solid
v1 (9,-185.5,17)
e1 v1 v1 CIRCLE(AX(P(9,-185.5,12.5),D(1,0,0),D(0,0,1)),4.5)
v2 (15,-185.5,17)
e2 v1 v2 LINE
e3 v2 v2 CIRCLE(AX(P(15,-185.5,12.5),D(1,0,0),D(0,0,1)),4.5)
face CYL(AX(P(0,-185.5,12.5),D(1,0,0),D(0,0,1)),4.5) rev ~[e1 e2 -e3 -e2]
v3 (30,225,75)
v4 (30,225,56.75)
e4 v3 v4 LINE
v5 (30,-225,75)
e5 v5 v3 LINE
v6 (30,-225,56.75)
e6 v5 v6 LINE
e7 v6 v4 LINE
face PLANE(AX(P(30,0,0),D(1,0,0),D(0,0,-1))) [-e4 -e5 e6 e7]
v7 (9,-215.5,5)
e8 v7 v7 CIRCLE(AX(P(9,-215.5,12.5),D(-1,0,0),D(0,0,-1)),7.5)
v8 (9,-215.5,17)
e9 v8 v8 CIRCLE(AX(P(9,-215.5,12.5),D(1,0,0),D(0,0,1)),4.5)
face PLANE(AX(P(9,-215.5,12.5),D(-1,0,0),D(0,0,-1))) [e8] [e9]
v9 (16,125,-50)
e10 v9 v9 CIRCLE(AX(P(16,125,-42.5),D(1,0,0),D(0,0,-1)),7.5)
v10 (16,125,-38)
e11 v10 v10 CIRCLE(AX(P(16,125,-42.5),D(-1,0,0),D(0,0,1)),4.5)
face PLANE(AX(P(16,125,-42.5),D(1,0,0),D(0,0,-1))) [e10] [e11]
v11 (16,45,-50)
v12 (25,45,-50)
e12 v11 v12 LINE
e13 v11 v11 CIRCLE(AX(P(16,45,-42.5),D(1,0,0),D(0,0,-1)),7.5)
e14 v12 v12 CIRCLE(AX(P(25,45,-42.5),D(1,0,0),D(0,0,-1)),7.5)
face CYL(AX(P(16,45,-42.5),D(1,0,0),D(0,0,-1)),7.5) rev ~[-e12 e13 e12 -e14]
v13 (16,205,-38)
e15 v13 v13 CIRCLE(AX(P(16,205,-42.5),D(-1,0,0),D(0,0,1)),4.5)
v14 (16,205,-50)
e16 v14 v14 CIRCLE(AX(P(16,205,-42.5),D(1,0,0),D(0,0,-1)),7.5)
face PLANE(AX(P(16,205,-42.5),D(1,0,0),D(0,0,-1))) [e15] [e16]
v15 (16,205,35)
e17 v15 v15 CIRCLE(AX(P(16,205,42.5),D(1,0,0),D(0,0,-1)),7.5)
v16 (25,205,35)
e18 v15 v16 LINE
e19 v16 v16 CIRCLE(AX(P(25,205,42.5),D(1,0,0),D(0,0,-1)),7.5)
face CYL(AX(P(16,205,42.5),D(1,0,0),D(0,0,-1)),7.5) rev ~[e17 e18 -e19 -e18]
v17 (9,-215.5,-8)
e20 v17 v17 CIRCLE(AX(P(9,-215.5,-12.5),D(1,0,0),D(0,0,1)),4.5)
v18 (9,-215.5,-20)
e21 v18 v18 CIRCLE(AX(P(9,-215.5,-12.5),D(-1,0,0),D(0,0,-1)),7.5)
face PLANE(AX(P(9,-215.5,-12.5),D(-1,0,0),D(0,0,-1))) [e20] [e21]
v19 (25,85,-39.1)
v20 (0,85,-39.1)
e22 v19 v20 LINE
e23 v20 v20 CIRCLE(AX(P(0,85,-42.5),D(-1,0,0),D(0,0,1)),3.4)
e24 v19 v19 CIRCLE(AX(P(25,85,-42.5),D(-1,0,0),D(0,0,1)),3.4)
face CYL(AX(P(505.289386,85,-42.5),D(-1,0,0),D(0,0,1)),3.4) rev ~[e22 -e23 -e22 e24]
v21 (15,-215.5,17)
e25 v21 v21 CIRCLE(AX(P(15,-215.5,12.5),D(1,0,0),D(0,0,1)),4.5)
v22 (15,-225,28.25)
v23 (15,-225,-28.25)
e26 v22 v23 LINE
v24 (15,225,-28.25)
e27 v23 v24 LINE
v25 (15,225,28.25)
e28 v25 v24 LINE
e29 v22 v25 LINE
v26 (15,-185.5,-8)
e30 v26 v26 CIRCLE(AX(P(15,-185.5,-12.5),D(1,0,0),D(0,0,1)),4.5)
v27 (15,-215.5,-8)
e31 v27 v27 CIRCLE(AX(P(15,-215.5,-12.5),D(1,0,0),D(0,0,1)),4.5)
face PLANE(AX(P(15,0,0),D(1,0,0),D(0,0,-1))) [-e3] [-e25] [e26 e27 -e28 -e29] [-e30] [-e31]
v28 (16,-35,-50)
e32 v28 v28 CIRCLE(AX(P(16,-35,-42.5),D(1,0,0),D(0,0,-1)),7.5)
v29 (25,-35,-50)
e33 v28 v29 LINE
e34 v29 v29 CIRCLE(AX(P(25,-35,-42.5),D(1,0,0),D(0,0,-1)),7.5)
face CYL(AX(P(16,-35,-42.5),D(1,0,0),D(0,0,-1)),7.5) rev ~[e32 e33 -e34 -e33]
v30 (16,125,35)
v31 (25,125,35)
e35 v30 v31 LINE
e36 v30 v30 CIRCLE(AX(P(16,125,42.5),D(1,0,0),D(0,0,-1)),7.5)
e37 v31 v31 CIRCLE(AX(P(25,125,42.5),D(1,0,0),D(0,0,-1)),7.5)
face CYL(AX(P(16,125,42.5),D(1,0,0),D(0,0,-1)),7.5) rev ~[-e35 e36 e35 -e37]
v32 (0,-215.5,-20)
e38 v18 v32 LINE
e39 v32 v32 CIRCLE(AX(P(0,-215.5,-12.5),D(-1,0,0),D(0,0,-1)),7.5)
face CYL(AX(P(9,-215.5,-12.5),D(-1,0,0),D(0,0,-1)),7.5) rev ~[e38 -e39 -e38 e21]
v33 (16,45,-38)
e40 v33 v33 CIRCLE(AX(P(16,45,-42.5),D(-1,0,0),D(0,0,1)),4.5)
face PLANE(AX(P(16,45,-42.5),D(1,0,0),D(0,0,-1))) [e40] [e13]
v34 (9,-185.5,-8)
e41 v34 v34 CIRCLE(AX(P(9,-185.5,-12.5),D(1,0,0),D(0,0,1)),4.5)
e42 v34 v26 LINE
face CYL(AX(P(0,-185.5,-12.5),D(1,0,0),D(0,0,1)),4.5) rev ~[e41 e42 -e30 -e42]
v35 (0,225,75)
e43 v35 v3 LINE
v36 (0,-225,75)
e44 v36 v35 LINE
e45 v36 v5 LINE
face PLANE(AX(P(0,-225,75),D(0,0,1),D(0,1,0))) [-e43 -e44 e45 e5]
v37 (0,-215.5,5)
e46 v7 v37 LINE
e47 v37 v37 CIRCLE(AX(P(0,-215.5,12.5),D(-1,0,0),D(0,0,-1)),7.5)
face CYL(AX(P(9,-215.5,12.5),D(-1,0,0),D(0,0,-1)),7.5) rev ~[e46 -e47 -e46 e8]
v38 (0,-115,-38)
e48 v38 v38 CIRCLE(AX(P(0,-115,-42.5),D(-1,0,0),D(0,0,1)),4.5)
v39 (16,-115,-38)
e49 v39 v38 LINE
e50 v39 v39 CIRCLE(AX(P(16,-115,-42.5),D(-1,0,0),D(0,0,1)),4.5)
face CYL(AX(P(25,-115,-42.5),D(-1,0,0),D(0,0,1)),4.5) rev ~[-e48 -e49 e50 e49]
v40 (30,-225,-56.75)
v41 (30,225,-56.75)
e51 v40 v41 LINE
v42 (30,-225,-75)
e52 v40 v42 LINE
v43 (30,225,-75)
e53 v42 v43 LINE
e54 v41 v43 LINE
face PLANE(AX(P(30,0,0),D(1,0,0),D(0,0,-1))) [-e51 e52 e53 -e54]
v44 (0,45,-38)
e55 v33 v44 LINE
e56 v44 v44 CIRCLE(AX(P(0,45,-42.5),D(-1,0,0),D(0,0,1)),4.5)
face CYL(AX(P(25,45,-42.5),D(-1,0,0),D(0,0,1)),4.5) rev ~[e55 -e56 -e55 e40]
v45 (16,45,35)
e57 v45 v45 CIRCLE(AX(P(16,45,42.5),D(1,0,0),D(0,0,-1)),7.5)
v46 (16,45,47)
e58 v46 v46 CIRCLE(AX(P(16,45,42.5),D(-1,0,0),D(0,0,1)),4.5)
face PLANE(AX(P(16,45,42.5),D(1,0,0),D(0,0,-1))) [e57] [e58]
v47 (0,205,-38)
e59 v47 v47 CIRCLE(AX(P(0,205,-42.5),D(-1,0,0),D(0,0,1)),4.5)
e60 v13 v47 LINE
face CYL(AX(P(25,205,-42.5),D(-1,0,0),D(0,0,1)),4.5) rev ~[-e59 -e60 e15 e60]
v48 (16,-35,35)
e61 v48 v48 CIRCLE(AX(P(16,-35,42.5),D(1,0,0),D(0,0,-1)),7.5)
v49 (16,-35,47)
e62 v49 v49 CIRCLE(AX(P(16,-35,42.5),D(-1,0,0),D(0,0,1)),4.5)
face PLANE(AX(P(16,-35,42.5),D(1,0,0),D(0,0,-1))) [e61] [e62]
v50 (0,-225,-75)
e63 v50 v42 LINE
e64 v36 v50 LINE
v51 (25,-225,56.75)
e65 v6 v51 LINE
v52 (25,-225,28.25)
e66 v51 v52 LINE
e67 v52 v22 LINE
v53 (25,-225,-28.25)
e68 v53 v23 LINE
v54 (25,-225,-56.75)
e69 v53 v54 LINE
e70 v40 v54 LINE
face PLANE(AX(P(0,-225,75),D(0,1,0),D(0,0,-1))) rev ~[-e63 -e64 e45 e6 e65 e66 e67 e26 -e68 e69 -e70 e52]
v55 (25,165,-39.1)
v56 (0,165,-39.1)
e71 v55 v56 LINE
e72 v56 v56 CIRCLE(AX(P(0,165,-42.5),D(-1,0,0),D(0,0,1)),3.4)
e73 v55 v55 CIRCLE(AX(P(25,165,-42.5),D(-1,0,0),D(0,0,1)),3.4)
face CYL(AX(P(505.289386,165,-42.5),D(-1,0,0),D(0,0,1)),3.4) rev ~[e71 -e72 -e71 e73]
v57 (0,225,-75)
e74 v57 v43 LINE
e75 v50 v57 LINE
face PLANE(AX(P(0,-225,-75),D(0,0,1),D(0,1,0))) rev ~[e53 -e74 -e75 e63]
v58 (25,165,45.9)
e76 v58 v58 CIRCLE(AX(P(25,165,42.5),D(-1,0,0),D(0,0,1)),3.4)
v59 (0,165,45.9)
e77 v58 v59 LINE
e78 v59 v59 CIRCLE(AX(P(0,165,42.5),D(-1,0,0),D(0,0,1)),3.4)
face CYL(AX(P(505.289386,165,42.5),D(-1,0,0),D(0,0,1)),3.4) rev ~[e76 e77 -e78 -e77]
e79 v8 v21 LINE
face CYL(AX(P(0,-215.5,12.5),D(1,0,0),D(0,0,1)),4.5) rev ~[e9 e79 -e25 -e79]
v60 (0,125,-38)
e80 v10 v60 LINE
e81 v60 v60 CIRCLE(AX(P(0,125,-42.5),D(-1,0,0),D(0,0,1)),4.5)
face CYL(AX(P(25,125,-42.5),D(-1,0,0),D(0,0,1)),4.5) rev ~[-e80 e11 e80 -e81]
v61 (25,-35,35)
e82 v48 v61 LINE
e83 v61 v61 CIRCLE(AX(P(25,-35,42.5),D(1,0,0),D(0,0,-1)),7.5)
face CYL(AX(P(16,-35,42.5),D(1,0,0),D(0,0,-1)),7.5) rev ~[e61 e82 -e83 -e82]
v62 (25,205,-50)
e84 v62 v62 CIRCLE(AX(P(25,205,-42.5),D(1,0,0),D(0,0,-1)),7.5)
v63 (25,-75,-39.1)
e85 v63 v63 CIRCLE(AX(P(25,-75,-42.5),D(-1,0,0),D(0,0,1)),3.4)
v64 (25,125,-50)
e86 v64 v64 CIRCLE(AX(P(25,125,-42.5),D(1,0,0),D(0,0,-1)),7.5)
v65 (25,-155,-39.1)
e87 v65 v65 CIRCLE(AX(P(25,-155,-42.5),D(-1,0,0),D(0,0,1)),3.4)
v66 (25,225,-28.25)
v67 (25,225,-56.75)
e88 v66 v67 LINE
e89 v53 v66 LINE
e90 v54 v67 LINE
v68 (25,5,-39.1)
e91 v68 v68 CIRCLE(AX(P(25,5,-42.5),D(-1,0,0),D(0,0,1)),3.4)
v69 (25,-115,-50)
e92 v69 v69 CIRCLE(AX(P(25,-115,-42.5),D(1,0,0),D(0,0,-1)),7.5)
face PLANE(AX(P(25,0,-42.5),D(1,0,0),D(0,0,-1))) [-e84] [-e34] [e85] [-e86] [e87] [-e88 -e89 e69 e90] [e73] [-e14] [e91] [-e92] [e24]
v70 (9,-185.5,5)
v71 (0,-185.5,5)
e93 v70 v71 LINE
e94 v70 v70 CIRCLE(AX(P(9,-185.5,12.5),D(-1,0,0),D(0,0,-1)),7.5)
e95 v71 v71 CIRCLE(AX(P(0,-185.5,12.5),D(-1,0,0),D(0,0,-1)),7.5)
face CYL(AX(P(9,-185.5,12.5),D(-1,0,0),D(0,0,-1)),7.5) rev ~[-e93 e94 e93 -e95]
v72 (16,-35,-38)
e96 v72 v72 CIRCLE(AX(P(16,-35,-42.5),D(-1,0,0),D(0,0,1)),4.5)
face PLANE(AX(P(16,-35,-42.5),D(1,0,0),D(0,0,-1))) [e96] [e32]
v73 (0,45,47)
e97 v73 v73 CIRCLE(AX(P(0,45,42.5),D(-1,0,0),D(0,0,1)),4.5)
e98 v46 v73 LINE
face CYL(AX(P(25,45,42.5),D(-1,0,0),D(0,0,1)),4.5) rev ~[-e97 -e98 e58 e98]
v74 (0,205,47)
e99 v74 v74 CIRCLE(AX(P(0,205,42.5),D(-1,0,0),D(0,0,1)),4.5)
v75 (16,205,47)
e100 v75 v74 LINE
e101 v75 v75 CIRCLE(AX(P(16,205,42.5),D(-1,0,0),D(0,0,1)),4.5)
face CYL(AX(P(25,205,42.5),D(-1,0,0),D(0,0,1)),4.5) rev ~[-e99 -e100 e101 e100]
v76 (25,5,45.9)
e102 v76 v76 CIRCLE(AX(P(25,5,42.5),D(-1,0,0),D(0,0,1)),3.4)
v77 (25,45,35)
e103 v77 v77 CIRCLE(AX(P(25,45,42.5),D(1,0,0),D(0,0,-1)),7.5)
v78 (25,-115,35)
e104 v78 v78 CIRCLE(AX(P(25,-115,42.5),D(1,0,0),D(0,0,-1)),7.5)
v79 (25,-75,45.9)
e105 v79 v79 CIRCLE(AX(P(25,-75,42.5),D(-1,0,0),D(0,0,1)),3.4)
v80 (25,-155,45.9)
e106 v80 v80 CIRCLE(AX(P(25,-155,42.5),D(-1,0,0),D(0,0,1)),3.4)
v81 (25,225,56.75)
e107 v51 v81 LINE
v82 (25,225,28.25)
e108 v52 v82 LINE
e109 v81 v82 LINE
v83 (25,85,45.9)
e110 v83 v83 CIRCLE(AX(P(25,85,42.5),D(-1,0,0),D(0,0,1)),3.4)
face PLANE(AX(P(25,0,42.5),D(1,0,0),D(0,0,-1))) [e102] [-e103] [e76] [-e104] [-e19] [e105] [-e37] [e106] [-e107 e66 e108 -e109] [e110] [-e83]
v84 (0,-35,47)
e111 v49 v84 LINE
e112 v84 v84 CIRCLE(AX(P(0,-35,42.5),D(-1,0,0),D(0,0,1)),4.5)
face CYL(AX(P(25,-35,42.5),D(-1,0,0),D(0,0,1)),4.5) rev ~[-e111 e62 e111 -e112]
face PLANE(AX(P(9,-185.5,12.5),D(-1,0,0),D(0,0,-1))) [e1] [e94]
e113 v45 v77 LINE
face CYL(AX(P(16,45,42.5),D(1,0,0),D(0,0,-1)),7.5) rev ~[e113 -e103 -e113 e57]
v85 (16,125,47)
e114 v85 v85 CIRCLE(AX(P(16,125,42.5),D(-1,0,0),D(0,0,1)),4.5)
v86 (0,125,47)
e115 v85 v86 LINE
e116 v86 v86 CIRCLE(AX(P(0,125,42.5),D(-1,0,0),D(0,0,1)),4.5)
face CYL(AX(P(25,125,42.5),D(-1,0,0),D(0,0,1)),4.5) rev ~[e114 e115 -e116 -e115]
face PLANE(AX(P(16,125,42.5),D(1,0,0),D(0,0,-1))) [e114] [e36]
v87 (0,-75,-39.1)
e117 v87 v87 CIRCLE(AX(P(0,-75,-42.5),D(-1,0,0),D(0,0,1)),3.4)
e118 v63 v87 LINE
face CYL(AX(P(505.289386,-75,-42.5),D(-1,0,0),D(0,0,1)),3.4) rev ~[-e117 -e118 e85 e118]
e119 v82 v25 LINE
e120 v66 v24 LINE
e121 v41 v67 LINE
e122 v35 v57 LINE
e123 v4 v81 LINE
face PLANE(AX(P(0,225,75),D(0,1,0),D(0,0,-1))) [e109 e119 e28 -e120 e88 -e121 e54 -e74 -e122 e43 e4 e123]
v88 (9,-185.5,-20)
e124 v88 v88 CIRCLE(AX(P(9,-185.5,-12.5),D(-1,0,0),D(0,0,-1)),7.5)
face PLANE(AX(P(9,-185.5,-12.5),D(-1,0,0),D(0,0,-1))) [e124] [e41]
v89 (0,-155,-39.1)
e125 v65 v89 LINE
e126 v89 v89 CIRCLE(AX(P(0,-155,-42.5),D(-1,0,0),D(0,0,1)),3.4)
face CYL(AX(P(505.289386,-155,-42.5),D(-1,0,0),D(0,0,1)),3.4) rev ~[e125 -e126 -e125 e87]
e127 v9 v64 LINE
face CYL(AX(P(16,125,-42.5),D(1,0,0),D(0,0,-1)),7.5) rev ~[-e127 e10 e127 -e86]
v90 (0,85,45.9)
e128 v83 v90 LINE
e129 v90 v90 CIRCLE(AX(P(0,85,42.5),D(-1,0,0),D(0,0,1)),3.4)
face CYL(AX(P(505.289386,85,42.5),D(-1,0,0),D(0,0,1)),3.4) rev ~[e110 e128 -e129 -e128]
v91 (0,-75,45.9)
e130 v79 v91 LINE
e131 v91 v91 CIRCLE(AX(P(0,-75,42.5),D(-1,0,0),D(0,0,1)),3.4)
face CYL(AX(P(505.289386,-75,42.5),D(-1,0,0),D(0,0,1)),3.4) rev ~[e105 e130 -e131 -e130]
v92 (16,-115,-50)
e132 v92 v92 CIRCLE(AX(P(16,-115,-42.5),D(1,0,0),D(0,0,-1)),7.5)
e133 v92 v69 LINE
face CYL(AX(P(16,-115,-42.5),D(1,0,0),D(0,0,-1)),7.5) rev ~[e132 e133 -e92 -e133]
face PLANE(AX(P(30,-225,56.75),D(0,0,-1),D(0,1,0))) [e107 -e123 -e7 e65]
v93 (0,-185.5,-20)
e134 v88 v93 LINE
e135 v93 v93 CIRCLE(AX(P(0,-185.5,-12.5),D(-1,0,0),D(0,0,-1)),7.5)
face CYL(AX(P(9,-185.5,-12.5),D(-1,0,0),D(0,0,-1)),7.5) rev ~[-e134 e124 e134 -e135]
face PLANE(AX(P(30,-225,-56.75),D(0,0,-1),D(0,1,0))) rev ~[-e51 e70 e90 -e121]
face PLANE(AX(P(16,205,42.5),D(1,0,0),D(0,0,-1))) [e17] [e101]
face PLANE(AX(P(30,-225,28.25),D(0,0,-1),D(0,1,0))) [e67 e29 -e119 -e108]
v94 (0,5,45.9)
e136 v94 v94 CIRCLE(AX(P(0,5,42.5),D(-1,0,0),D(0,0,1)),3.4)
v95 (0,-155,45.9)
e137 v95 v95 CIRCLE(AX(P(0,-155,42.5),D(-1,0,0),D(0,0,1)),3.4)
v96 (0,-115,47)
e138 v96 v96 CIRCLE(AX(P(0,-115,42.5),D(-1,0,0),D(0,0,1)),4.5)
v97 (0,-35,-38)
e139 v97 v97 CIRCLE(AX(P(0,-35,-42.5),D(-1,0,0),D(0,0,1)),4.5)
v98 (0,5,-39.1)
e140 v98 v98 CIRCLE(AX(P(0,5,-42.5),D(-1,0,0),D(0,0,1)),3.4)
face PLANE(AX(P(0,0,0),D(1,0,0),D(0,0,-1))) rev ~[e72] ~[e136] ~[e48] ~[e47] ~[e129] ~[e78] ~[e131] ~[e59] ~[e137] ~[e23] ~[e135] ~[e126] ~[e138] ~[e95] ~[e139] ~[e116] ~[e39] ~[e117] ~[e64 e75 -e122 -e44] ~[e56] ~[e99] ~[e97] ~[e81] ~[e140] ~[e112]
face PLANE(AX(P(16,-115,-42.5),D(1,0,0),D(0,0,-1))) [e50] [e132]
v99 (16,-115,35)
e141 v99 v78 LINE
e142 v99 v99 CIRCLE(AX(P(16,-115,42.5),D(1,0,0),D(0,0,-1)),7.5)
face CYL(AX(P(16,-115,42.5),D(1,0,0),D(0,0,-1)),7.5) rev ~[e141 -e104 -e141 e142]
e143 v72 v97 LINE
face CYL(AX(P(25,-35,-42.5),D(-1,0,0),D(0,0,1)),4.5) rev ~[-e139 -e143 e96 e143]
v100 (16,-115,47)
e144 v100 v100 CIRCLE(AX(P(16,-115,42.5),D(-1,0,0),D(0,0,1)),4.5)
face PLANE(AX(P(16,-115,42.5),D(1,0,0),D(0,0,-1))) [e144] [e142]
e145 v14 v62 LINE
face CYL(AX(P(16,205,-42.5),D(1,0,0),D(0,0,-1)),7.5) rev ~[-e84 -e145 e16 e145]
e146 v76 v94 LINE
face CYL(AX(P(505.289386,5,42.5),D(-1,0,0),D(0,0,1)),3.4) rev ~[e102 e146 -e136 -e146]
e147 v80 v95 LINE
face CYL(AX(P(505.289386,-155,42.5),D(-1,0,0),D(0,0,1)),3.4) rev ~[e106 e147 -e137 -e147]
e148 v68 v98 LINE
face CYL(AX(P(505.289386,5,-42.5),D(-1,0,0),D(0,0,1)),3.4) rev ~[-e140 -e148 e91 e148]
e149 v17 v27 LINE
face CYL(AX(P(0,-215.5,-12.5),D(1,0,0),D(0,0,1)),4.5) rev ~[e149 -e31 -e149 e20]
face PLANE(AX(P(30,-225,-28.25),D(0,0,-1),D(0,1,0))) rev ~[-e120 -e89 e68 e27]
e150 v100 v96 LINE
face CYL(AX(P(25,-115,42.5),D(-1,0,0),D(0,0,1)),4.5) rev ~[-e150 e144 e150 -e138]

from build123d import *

# Parameters (mm, degrees)
SKETCH_1_W                = 150
SKETCH_1_H                = 450
EXTRUDE_1_DEPTH           = 30
SKETCH_2_W                = 28.5
SKETCH_2_H                = 450
CUT_EXTRUDE_1_DEPTH       = 5
HOLE_WIZARD_M8_1_D        = 6.8
PATTERN_LINEAR_1_COUNT    = 5
PATTERN_LINEAR_1_PITCH    = 80
HOLE_WIZARD_1_D           = 9
HOLE_WIZARD_1_CBORE_D     = 15
HOLE_WIZARD_1_CBORE_DEPTH = 9
PATTERN_LINEAR_2_COUNT    = 5
PATTERN_LINEAR_2_PITCH    = 80
SKETCH_7_W                = 56.5
SKETCH_7_H                = 450
CUT_EXTRUDE_2_DEPTH       = 15
HOLE_WIZARD_2_D           = 9
HOLE_WIZARD_2_CBORE_D     = 15
HOLE_WIZARD_2_CBORE_DEPTH = 9


with BuildPart() as part:
    # 草图1 → 凸台-拉伸1 (new body)
    with BuildSketch(Plane(origin=(0, 0, 0), x_dir=(0, 0, -1), z_dir=(1, 0, 0))):
        Rectangle(SKETCH_1_W, SKETCH_1_H)
    extrude(amount=EXTRUDE_1_DEPTH)

    # 草图2 → 切除-拉伸1 (cut)
    with BuildSketch(Plane(origin=(30, 0, 0), x_dir=(0, 0, -1), z_dir=(1, 0, 0))):
        with Locations((-42.5, 0)):
            Rectangle(SKETCH_2_W, SKETCH_2_H)
        with Locations((42.5, 0)):
            Rectangle(SKETCH_2_W, SKETCH_2_H)
    extrude(amount=-CUT_EXTRUDE_1_DEPTH, mode=Mode.SUBTRACT)

    # M8 螺纹孔1 (through all)
    with Locations(Plane(origin=(30, 0, 0), x_dir=(0, 0, -1), z_dir=(1, 0, 0))):
        with Locations((-42.5, -155), (42.5, -155)):
            hole_wizard_m8_1 = Hole(HOLE_WIZARD_M8_1_D / 2)

    # 阵列(线性)1: M8 螺纹孔1 ×5
    with Locations(*[(0, i * PATTERN_LINEAR_1_PITCH, 0) for i in range(1, PATTERN_LINEAR_1_COUNT)]):
        add(hole_wizard_m8_1, mode=Mode.SUBTRACT)

    # 打孔尺寸(%根据)内六角圆柱头螺钉的类型1 (through all)
    with Locations(Plane(origin=(25, 0, 0), x_dir=(0, 0, -1), z_dir=(1, 0, 0))):
        with Locations((-42.5, -115), (42.5, -115)):
            hole_wizard_1 = CounterBoreHole(HOLE_WIZARD_1_D / 2, HOLE_WIZARD_1_CBORE_D / 2, HOLE_WIZARD_1_CBORE_DEPTH)

    # 阵列(线性)2: 打孔尺寸(%根据)内六角圆柱头螺钉的类型1 ×5
    with Locations(*[(0, i * PATTERN_LINEAR_2_PITCH, 0) for i in range(1, PATTERN_LINEAR_2_COUNT)]):
        add(hole_wizard_1, mode=Mode.SUBTRACT)

    # 草图7 → 切除-拉伸2 (cut)
    with BuildSketch(Plane(origin=(30, 0, 0), x_dir=(0, 0, -1), z_dir=(1, 0, 0))):
        Rectangle(SKETCH_7_W, SKETCH_7_H)
    extrude(amount=-CUT_EXTRUDE_2_DEPTH, mode=Mode.SUBTRACT)

    # 打孔尺寸(%根据)内六角圆柱头螺钉的类型2 (through all)
    with Locations(Plane(origin=(0, 0, 0), x_dir=(0, 0, -1), z_dir=(-1, 0, 0))):
        with Locations((-12.5, 185.5), (12.5, 185.5), (-12.5, 215.5), (12.5, 215.5)):
            CounterBoreHole(HOLE_WIZARD_2_D / 2, HOLE_WIZARD_2_CBORE_D / 2, HOLE_WIZARD_2_CBORE_DEPTH)


solid = part.part
